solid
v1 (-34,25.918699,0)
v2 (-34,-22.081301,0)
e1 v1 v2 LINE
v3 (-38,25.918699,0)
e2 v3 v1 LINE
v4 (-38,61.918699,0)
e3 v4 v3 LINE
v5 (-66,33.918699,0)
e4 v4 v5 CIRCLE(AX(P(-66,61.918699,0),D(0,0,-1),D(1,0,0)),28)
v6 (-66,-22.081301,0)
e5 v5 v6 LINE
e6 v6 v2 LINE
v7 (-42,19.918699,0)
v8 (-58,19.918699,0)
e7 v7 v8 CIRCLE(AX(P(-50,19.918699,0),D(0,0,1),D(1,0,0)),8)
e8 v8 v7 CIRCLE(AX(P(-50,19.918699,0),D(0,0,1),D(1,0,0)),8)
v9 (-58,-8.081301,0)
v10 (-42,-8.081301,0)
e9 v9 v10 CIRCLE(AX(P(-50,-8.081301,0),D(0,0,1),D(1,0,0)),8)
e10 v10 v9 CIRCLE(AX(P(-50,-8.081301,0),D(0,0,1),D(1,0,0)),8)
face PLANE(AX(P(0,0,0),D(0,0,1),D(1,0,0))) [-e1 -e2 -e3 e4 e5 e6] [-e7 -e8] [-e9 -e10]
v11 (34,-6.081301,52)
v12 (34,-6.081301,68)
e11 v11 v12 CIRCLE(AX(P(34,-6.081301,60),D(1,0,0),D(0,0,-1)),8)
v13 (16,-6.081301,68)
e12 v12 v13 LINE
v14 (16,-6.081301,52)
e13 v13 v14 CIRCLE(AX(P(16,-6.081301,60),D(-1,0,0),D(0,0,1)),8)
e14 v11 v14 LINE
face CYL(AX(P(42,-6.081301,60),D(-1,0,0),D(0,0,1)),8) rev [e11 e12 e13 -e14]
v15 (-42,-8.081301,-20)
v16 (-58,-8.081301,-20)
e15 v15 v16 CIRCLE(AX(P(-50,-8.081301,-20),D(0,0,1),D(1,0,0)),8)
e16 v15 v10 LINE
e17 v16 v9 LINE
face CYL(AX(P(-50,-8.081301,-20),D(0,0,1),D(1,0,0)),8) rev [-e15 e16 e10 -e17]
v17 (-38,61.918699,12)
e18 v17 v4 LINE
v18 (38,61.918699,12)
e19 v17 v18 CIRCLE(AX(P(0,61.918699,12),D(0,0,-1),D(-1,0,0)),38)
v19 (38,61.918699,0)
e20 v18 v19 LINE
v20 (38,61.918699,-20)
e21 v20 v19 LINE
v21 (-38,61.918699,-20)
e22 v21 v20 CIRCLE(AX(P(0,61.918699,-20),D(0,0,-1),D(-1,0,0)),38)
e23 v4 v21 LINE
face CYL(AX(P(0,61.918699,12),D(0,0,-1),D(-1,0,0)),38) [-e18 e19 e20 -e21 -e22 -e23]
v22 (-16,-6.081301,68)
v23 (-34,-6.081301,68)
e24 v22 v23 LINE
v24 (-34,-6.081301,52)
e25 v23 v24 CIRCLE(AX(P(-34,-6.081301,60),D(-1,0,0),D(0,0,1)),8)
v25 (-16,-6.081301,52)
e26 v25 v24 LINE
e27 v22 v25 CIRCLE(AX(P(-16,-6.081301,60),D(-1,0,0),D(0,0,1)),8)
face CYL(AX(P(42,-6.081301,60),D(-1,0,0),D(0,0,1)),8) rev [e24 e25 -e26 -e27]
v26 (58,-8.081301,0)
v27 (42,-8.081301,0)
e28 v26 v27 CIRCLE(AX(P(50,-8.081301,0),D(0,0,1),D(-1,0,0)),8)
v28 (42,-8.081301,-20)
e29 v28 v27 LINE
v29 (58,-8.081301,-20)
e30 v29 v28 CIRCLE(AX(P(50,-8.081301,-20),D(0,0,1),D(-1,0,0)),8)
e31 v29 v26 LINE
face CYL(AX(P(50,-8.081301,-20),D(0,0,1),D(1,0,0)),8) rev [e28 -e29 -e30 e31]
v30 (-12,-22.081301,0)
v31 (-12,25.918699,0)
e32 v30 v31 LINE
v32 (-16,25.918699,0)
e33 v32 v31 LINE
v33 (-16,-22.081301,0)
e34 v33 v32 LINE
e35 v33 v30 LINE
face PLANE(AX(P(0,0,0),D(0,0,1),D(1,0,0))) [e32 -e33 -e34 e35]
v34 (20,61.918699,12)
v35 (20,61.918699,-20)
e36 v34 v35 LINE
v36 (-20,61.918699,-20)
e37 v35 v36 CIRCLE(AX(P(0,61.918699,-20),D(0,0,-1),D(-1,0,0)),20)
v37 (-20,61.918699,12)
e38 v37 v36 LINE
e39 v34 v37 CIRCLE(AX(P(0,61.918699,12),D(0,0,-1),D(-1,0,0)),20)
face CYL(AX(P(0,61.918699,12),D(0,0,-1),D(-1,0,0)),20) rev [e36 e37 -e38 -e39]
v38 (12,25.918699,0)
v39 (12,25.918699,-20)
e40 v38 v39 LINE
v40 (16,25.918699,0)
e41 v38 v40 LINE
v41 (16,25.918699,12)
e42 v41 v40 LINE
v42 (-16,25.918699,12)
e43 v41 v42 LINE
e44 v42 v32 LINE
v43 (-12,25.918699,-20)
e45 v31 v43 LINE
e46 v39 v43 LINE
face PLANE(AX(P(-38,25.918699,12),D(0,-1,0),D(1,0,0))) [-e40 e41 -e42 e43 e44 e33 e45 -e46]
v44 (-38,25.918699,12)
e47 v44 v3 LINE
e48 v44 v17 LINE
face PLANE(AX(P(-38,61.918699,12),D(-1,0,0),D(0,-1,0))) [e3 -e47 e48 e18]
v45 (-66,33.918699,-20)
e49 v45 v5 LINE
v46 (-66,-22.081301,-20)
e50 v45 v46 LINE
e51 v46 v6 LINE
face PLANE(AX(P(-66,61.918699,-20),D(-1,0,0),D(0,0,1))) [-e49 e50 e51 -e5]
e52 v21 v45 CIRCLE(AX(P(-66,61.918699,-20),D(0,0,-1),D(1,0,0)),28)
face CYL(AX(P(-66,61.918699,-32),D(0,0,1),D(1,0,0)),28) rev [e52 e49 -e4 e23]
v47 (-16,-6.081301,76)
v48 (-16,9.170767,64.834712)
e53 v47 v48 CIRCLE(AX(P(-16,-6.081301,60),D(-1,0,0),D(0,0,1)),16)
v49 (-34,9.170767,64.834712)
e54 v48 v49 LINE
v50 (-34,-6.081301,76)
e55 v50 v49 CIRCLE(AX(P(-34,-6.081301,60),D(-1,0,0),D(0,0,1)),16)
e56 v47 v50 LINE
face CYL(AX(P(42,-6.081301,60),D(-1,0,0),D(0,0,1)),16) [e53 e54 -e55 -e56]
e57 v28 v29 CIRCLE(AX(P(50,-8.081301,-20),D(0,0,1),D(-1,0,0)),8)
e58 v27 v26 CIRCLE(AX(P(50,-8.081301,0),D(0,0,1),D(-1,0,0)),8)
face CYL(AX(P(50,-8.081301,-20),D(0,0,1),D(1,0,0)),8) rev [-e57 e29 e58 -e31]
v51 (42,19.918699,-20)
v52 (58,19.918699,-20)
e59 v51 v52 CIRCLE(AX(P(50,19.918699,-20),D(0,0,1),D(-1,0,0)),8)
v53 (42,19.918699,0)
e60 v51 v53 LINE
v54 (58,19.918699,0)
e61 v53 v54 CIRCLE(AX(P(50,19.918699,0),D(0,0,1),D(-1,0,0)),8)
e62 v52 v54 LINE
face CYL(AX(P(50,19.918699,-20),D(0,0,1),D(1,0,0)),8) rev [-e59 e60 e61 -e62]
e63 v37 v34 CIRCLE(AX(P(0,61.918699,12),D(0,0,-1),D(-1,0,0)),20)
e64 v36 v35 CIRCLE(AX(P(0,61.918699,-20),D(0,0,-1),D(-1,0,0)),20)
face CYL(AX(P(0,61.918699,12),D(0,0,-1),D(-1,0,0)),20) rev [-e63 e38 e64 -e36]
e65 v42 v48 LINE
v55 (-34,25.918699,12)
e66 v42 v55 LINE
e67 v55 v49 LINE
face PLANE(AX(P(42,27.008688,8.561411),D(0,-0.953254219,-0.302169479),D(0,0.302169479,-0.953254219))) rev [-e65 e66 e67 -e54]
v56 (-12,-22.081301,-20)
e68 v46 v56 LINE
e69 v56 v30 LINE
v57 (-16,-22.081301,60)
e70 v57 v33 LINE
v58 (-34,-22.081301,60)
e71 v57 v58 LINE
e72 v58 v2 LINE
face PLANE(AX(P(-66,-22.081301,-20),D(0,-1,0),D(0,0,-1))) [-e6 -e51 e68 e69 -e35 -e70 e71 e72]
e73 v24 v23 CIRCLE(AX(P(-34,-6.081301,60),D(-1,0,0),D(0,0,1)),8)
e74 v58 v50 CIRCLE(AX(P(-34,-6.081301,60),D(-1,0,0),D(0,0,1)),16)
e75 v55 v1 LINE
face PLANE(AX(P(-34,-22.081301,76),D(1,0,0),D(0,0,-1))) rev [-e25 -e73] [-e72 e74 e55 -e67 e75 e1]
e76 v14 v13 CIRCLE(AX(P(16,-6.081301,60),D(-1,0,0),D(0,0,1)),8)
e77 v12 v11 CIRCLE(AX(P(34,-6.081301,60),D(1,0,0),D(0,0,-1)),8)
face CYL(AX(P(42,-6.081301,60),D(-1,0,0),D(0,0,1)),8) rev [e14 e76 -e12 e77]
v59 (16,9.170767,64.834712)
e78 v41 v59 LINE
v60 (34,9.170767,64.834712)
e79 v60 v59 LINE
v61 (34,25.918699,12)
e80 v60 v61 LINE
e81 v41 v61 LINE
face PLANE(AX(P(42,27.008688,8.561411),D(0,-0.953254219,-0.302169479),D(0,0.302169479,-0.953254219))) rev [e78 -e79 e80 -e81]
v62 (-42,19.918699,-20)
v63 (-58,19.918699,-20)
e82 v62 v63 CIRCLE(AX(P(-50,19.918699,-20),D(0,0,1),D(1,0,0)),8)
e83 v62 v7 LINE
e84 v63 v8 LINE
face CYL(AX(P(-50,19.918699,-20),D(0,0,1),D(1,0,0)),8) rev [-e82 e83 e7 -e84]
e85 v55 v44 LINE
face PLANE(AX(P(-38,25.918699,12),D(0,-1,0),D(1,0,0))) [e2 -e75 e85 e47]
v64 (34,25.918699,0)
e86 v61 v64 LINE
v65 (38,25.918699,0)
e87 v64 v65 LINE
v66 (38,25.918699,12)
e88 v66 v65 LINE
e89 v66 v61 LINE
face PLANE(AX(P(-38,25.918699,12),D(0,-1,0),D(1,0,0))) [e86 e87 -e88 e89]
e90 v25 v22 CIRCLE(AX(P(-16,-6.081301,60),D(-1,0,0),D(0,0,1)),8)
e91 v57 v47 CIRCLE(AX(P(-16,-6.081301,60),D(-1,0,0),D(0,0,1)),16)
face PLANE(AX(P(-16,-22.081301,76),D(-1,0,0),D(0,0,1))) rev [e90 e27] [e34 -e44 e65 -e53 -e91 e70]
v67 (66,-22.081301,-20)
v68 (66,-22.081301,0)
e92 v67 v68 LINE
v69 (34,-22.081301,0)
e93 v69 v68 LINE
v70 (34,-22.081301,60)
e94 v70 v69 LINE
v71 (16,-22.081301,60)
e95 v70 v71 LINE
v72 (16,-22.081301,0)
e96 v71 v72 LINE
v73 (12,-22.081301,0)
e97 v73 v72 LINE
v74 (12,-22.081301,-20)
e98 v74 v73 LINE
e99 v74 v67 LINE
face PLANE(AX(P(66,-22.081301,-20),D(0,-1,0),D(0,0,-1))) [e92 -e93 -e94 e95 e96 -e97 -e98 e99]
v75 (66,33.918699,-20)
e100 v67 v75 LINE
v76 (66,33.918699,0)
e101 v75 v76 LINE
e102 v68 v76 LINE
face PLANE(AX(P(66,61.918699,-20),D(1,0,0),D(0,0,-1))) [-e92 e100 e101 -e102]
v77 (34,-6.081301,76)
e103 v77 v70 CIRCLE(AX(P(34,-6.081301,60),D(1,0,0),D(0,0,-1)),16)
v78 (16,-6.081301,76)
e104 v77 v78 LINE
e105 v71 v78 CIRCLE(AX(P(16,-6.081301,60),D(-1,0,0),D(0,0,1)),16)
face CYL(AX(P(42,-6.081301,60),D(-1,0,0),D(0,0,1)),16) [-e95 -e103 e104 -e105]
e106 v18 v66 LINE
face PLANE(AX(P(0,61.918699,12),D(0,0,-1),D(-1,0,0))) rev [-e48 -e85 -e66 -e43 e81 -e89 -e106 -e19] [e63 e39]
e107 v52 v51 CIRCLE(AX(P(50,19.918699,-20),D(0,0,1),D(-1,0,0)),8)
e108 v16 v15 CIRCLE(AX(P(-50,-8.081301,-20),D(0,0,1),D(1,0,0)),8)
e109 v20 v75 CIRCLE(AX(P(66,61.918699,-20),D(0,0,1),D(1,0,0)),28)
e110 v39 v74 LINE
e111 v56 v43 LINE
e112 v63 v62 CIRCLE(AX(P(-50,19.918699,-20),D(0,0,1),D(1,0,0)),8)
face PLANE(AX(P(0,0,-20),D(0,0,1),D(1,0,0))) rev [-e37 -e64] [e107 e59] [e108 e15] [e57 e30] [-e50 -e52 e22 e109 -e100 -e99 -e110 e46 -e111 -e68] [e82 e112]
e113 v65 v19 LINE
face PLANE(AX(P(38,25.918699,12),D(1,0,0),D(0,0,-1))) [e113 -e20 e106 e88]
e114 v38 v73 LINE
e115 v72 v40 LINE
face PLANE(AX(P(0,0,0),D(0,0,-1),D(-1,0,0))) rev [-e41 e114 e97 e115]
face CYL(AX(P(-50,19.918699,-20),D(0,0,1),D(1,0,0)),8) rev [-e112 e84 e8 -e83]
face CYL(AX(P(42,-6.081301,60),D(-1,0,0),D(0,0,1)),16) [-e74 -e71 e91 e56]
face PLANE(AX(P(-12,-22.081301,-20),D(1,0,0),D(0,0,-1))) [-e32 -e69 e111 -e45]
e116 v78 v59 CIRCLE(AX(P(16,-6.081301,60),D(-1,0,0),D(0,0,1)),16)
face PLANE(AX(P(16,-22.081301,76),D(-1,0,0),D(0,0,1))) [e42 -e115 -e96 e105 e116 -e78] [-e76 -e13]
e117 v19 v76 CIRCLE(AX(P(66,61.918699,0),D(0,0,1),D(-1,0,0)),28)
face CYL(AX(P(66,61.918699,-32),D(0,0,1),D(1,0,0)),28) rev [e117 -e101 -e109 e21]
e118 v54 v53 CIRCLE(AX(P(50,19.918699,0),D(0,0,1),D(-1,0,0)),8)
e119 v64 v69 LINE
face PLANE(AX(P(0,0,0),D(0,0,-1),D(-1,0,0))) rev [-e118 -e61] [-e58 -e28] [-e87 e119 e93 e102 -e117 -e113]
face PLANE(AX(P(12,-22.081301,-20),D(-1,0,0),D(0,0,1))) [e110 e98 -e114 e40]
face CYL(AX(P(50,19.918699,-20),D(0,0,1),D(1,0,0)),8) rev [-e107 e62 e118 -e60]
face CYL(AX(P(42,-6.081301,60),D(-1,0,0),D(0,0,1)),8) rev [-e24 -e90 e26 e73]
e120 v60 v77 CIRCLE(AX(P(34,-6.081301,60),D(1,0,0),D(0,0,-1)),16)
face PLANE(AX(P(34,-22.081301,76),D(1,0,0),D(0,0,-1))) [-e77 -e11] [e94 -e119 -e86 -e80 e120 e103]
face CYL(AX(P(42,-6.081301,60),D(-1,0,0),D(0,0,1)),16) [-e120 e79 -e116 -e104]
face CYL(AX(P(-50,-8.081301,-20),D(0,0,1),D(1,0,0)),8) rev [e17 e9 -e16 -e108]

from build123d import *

# Parameters (mm, degrees)
BASE_PLATE_SKETCH_W       = 54
BASE_PLATE_SKETCH_H       = 84
BASE_PLATE_SKETCH_R       = 8
BASE_PLATE_DEPTH          = 20
BASE_PLATE_2_DEPTH        = 20
BEARING_BOSS_SKETCH_R     = 20
BEARING_BOSS_DEPTH        = 32
BORE_START                = -32
BORE_SKETCH_R             = 20
BORE_40_DEPTH             = 32
SIDE_CUT_DEPTH            = 32
CLEVIS_LUG_SKETCH_W       = 18
CLEVIS_LUG_SKETCH_H       = 48
CLEVIS_LUG_DEPTH          = 76
LUG_END_PROFILE_SKETCH_R  = 8
LUG_END_PROFILE_CUT_DEPTH = 76


with BuildPart() as part:
    # Base Plate Sketch → Base Plate (new body)
    with BuildSketch(Plane.XY):
        with Locations((-39, 19.918699187)):
            Rectangle(BASE_PLATE_SKETCH_W, BASE_PLATE_SKETCH_H)
        with Locations((-50, 19.918699187)):
            Circle(BASE_PLATE_SKETCH_R, mode=Mode.SUBTRACT)
        with Locations((-50, -8.081300813)):
            Circle(BASE_PLATE_SKETCH_R, mode=Mode.SUBTRACT)
    extrude(amount=-BASE_PLATE_DEPTH)



with BuildPart() as body_2:
    # Base Plate Sketch → Base Plate 2 (new body)
    with BuildSketch(Plane.XY):
        with Locations((39, 19.918699187)):
            Rectangle(BASE_PLATE_SKETCH_W, BASE_PLATE_SKETCH_H)
        with Locations(Location((50, -8.081300813, 0), (0, 0, 180))):
            Circle(BASE_PLATE_SKETCH_R, mode=Mode.SUBTRACT)
        with Locations(Location((50, 19.918699187, 0), (0, 0, 180))):
            Circle(BASE_PLATE_SKETCH_R, mode=Mode.SUBTRACT)
    extrude(amount=-BASE_PLATE_2_DEPTH)


with BuildPart() as part_1:
    add(part.part)

    add(body_2.part)  # Bearing Boss merges body 2
    # Bearing Boss Sketch → Bearing Boss (add)
    with BuildSketch(Plane(origin=(0, 0, -20), x_dir=(-1, 0, 0), z_dir=(0, 0, -1))):
        with BuildLine():
            Line((38, 61.918699187), (38, 25.918699187))
            Line((38, 25.918699187), (-38, 25.918699187))
            Line((-38, 25.918699187), (-38, 61.918699187))
            ThreePointArc((-38, 61.918699187), (0, 99.918699187), (38, 61.918699187))
        make_face()
        with Locations((0, 61.918699187)):
            Circle(BEARING_BOSS_SKETCH_R, mode=Mode.SUBTRACT)
    extrude(amount=-BEARING_BOSS_DEPTH)

    # Bore Sketch → Bore Ø40 (cut)
    with BuildSketch(Plane.XY.offset(12).offset(BORE_START)):
        with Locations(Location((0, 61.918699187, 0), (0, 0, 180))):
            Circle(BORE_SKETCH_R)
    extrude(amount=BORE_40_DEPTH, mode=Mode.SUBTRACT)

    # Side Cut Sketch → Side Cut (cut)
    with BuildSketch(Plane.XY):
        with BuildLine():
            ThreePointArc((-66, 33.918699187), (-46.201010127, 42.119709314), (-38, 61.918699187))
            Line((-38, 61.918699187), (-66, 61.918699187))
            Line((-66, 61.918699187), (-66, 33.918699187))
        make_face()
    side_cut = extrude(amount=-SIDE_CUT_DEPTH, mode=Mode.SUBTRACT)

    # Side Cut Mirror: Side Cut across plane
    add(side_cut.mirror(Plane(origin=(0, 0, 0), x_dir=(0, 0, 1), z_dir=(1, 0, 0))), mode=Mode.SUBTRACT)

    # Clevis Lug Sketch → Clevis Lug (add)
    with BuildSketch(Plane.XY):
        with Locations((-25, 1.918699187)):
            Rectangle(CLEVIS_LUG_SKETCH_W, CLEVIS_LUG_SKETCH_H)
    clevis_lug = extrude(amount=CLEVIS_LUG_DEPTH)

    # Clevis Lug Mirror: Clevis Lug across plane
    add(clevis_lug.mirror(Plane(origin=(0, 0, 0), x_dir=(0, 0, 1), z_dir=(1, 0, 0))))

    # Lug End Profile Sketch → Lug End Profile Cut (cut)
    with BuildSketch(Plane.ZY.offset(34)):
        with BuildLine():
            Line((76, 25.918699187), (12, 25.918699187))
            Line((12, 25.918699187), (64.834711668, 9.170766689))
            ThreePointArc((64.834711668, 9.170766689), (72.910371542, 3.3697471), (76, -6.081300813))
            Line((76, -6.081300813), (76, 25.918699187))
        make_face()
        with BuildLine():
            Line((76, -22.081300813), (76, -6.081300813))
            ThreePointArc((76, -6.081300813), (71.313708499, -17.395009312), (60, -22.081300813))
            Line((60, -22.081300813), (76, -22.081300813))
        make_face()
        with Locations((60, -6.081300813)):
            Circle(LUG_END_PROFILE_SKETCH_R)
    extrude(amount=-LUG_END_PROFILE_CUT_DEPTH, mode=Mode.SUBTRACT)


solid = part_1.part
